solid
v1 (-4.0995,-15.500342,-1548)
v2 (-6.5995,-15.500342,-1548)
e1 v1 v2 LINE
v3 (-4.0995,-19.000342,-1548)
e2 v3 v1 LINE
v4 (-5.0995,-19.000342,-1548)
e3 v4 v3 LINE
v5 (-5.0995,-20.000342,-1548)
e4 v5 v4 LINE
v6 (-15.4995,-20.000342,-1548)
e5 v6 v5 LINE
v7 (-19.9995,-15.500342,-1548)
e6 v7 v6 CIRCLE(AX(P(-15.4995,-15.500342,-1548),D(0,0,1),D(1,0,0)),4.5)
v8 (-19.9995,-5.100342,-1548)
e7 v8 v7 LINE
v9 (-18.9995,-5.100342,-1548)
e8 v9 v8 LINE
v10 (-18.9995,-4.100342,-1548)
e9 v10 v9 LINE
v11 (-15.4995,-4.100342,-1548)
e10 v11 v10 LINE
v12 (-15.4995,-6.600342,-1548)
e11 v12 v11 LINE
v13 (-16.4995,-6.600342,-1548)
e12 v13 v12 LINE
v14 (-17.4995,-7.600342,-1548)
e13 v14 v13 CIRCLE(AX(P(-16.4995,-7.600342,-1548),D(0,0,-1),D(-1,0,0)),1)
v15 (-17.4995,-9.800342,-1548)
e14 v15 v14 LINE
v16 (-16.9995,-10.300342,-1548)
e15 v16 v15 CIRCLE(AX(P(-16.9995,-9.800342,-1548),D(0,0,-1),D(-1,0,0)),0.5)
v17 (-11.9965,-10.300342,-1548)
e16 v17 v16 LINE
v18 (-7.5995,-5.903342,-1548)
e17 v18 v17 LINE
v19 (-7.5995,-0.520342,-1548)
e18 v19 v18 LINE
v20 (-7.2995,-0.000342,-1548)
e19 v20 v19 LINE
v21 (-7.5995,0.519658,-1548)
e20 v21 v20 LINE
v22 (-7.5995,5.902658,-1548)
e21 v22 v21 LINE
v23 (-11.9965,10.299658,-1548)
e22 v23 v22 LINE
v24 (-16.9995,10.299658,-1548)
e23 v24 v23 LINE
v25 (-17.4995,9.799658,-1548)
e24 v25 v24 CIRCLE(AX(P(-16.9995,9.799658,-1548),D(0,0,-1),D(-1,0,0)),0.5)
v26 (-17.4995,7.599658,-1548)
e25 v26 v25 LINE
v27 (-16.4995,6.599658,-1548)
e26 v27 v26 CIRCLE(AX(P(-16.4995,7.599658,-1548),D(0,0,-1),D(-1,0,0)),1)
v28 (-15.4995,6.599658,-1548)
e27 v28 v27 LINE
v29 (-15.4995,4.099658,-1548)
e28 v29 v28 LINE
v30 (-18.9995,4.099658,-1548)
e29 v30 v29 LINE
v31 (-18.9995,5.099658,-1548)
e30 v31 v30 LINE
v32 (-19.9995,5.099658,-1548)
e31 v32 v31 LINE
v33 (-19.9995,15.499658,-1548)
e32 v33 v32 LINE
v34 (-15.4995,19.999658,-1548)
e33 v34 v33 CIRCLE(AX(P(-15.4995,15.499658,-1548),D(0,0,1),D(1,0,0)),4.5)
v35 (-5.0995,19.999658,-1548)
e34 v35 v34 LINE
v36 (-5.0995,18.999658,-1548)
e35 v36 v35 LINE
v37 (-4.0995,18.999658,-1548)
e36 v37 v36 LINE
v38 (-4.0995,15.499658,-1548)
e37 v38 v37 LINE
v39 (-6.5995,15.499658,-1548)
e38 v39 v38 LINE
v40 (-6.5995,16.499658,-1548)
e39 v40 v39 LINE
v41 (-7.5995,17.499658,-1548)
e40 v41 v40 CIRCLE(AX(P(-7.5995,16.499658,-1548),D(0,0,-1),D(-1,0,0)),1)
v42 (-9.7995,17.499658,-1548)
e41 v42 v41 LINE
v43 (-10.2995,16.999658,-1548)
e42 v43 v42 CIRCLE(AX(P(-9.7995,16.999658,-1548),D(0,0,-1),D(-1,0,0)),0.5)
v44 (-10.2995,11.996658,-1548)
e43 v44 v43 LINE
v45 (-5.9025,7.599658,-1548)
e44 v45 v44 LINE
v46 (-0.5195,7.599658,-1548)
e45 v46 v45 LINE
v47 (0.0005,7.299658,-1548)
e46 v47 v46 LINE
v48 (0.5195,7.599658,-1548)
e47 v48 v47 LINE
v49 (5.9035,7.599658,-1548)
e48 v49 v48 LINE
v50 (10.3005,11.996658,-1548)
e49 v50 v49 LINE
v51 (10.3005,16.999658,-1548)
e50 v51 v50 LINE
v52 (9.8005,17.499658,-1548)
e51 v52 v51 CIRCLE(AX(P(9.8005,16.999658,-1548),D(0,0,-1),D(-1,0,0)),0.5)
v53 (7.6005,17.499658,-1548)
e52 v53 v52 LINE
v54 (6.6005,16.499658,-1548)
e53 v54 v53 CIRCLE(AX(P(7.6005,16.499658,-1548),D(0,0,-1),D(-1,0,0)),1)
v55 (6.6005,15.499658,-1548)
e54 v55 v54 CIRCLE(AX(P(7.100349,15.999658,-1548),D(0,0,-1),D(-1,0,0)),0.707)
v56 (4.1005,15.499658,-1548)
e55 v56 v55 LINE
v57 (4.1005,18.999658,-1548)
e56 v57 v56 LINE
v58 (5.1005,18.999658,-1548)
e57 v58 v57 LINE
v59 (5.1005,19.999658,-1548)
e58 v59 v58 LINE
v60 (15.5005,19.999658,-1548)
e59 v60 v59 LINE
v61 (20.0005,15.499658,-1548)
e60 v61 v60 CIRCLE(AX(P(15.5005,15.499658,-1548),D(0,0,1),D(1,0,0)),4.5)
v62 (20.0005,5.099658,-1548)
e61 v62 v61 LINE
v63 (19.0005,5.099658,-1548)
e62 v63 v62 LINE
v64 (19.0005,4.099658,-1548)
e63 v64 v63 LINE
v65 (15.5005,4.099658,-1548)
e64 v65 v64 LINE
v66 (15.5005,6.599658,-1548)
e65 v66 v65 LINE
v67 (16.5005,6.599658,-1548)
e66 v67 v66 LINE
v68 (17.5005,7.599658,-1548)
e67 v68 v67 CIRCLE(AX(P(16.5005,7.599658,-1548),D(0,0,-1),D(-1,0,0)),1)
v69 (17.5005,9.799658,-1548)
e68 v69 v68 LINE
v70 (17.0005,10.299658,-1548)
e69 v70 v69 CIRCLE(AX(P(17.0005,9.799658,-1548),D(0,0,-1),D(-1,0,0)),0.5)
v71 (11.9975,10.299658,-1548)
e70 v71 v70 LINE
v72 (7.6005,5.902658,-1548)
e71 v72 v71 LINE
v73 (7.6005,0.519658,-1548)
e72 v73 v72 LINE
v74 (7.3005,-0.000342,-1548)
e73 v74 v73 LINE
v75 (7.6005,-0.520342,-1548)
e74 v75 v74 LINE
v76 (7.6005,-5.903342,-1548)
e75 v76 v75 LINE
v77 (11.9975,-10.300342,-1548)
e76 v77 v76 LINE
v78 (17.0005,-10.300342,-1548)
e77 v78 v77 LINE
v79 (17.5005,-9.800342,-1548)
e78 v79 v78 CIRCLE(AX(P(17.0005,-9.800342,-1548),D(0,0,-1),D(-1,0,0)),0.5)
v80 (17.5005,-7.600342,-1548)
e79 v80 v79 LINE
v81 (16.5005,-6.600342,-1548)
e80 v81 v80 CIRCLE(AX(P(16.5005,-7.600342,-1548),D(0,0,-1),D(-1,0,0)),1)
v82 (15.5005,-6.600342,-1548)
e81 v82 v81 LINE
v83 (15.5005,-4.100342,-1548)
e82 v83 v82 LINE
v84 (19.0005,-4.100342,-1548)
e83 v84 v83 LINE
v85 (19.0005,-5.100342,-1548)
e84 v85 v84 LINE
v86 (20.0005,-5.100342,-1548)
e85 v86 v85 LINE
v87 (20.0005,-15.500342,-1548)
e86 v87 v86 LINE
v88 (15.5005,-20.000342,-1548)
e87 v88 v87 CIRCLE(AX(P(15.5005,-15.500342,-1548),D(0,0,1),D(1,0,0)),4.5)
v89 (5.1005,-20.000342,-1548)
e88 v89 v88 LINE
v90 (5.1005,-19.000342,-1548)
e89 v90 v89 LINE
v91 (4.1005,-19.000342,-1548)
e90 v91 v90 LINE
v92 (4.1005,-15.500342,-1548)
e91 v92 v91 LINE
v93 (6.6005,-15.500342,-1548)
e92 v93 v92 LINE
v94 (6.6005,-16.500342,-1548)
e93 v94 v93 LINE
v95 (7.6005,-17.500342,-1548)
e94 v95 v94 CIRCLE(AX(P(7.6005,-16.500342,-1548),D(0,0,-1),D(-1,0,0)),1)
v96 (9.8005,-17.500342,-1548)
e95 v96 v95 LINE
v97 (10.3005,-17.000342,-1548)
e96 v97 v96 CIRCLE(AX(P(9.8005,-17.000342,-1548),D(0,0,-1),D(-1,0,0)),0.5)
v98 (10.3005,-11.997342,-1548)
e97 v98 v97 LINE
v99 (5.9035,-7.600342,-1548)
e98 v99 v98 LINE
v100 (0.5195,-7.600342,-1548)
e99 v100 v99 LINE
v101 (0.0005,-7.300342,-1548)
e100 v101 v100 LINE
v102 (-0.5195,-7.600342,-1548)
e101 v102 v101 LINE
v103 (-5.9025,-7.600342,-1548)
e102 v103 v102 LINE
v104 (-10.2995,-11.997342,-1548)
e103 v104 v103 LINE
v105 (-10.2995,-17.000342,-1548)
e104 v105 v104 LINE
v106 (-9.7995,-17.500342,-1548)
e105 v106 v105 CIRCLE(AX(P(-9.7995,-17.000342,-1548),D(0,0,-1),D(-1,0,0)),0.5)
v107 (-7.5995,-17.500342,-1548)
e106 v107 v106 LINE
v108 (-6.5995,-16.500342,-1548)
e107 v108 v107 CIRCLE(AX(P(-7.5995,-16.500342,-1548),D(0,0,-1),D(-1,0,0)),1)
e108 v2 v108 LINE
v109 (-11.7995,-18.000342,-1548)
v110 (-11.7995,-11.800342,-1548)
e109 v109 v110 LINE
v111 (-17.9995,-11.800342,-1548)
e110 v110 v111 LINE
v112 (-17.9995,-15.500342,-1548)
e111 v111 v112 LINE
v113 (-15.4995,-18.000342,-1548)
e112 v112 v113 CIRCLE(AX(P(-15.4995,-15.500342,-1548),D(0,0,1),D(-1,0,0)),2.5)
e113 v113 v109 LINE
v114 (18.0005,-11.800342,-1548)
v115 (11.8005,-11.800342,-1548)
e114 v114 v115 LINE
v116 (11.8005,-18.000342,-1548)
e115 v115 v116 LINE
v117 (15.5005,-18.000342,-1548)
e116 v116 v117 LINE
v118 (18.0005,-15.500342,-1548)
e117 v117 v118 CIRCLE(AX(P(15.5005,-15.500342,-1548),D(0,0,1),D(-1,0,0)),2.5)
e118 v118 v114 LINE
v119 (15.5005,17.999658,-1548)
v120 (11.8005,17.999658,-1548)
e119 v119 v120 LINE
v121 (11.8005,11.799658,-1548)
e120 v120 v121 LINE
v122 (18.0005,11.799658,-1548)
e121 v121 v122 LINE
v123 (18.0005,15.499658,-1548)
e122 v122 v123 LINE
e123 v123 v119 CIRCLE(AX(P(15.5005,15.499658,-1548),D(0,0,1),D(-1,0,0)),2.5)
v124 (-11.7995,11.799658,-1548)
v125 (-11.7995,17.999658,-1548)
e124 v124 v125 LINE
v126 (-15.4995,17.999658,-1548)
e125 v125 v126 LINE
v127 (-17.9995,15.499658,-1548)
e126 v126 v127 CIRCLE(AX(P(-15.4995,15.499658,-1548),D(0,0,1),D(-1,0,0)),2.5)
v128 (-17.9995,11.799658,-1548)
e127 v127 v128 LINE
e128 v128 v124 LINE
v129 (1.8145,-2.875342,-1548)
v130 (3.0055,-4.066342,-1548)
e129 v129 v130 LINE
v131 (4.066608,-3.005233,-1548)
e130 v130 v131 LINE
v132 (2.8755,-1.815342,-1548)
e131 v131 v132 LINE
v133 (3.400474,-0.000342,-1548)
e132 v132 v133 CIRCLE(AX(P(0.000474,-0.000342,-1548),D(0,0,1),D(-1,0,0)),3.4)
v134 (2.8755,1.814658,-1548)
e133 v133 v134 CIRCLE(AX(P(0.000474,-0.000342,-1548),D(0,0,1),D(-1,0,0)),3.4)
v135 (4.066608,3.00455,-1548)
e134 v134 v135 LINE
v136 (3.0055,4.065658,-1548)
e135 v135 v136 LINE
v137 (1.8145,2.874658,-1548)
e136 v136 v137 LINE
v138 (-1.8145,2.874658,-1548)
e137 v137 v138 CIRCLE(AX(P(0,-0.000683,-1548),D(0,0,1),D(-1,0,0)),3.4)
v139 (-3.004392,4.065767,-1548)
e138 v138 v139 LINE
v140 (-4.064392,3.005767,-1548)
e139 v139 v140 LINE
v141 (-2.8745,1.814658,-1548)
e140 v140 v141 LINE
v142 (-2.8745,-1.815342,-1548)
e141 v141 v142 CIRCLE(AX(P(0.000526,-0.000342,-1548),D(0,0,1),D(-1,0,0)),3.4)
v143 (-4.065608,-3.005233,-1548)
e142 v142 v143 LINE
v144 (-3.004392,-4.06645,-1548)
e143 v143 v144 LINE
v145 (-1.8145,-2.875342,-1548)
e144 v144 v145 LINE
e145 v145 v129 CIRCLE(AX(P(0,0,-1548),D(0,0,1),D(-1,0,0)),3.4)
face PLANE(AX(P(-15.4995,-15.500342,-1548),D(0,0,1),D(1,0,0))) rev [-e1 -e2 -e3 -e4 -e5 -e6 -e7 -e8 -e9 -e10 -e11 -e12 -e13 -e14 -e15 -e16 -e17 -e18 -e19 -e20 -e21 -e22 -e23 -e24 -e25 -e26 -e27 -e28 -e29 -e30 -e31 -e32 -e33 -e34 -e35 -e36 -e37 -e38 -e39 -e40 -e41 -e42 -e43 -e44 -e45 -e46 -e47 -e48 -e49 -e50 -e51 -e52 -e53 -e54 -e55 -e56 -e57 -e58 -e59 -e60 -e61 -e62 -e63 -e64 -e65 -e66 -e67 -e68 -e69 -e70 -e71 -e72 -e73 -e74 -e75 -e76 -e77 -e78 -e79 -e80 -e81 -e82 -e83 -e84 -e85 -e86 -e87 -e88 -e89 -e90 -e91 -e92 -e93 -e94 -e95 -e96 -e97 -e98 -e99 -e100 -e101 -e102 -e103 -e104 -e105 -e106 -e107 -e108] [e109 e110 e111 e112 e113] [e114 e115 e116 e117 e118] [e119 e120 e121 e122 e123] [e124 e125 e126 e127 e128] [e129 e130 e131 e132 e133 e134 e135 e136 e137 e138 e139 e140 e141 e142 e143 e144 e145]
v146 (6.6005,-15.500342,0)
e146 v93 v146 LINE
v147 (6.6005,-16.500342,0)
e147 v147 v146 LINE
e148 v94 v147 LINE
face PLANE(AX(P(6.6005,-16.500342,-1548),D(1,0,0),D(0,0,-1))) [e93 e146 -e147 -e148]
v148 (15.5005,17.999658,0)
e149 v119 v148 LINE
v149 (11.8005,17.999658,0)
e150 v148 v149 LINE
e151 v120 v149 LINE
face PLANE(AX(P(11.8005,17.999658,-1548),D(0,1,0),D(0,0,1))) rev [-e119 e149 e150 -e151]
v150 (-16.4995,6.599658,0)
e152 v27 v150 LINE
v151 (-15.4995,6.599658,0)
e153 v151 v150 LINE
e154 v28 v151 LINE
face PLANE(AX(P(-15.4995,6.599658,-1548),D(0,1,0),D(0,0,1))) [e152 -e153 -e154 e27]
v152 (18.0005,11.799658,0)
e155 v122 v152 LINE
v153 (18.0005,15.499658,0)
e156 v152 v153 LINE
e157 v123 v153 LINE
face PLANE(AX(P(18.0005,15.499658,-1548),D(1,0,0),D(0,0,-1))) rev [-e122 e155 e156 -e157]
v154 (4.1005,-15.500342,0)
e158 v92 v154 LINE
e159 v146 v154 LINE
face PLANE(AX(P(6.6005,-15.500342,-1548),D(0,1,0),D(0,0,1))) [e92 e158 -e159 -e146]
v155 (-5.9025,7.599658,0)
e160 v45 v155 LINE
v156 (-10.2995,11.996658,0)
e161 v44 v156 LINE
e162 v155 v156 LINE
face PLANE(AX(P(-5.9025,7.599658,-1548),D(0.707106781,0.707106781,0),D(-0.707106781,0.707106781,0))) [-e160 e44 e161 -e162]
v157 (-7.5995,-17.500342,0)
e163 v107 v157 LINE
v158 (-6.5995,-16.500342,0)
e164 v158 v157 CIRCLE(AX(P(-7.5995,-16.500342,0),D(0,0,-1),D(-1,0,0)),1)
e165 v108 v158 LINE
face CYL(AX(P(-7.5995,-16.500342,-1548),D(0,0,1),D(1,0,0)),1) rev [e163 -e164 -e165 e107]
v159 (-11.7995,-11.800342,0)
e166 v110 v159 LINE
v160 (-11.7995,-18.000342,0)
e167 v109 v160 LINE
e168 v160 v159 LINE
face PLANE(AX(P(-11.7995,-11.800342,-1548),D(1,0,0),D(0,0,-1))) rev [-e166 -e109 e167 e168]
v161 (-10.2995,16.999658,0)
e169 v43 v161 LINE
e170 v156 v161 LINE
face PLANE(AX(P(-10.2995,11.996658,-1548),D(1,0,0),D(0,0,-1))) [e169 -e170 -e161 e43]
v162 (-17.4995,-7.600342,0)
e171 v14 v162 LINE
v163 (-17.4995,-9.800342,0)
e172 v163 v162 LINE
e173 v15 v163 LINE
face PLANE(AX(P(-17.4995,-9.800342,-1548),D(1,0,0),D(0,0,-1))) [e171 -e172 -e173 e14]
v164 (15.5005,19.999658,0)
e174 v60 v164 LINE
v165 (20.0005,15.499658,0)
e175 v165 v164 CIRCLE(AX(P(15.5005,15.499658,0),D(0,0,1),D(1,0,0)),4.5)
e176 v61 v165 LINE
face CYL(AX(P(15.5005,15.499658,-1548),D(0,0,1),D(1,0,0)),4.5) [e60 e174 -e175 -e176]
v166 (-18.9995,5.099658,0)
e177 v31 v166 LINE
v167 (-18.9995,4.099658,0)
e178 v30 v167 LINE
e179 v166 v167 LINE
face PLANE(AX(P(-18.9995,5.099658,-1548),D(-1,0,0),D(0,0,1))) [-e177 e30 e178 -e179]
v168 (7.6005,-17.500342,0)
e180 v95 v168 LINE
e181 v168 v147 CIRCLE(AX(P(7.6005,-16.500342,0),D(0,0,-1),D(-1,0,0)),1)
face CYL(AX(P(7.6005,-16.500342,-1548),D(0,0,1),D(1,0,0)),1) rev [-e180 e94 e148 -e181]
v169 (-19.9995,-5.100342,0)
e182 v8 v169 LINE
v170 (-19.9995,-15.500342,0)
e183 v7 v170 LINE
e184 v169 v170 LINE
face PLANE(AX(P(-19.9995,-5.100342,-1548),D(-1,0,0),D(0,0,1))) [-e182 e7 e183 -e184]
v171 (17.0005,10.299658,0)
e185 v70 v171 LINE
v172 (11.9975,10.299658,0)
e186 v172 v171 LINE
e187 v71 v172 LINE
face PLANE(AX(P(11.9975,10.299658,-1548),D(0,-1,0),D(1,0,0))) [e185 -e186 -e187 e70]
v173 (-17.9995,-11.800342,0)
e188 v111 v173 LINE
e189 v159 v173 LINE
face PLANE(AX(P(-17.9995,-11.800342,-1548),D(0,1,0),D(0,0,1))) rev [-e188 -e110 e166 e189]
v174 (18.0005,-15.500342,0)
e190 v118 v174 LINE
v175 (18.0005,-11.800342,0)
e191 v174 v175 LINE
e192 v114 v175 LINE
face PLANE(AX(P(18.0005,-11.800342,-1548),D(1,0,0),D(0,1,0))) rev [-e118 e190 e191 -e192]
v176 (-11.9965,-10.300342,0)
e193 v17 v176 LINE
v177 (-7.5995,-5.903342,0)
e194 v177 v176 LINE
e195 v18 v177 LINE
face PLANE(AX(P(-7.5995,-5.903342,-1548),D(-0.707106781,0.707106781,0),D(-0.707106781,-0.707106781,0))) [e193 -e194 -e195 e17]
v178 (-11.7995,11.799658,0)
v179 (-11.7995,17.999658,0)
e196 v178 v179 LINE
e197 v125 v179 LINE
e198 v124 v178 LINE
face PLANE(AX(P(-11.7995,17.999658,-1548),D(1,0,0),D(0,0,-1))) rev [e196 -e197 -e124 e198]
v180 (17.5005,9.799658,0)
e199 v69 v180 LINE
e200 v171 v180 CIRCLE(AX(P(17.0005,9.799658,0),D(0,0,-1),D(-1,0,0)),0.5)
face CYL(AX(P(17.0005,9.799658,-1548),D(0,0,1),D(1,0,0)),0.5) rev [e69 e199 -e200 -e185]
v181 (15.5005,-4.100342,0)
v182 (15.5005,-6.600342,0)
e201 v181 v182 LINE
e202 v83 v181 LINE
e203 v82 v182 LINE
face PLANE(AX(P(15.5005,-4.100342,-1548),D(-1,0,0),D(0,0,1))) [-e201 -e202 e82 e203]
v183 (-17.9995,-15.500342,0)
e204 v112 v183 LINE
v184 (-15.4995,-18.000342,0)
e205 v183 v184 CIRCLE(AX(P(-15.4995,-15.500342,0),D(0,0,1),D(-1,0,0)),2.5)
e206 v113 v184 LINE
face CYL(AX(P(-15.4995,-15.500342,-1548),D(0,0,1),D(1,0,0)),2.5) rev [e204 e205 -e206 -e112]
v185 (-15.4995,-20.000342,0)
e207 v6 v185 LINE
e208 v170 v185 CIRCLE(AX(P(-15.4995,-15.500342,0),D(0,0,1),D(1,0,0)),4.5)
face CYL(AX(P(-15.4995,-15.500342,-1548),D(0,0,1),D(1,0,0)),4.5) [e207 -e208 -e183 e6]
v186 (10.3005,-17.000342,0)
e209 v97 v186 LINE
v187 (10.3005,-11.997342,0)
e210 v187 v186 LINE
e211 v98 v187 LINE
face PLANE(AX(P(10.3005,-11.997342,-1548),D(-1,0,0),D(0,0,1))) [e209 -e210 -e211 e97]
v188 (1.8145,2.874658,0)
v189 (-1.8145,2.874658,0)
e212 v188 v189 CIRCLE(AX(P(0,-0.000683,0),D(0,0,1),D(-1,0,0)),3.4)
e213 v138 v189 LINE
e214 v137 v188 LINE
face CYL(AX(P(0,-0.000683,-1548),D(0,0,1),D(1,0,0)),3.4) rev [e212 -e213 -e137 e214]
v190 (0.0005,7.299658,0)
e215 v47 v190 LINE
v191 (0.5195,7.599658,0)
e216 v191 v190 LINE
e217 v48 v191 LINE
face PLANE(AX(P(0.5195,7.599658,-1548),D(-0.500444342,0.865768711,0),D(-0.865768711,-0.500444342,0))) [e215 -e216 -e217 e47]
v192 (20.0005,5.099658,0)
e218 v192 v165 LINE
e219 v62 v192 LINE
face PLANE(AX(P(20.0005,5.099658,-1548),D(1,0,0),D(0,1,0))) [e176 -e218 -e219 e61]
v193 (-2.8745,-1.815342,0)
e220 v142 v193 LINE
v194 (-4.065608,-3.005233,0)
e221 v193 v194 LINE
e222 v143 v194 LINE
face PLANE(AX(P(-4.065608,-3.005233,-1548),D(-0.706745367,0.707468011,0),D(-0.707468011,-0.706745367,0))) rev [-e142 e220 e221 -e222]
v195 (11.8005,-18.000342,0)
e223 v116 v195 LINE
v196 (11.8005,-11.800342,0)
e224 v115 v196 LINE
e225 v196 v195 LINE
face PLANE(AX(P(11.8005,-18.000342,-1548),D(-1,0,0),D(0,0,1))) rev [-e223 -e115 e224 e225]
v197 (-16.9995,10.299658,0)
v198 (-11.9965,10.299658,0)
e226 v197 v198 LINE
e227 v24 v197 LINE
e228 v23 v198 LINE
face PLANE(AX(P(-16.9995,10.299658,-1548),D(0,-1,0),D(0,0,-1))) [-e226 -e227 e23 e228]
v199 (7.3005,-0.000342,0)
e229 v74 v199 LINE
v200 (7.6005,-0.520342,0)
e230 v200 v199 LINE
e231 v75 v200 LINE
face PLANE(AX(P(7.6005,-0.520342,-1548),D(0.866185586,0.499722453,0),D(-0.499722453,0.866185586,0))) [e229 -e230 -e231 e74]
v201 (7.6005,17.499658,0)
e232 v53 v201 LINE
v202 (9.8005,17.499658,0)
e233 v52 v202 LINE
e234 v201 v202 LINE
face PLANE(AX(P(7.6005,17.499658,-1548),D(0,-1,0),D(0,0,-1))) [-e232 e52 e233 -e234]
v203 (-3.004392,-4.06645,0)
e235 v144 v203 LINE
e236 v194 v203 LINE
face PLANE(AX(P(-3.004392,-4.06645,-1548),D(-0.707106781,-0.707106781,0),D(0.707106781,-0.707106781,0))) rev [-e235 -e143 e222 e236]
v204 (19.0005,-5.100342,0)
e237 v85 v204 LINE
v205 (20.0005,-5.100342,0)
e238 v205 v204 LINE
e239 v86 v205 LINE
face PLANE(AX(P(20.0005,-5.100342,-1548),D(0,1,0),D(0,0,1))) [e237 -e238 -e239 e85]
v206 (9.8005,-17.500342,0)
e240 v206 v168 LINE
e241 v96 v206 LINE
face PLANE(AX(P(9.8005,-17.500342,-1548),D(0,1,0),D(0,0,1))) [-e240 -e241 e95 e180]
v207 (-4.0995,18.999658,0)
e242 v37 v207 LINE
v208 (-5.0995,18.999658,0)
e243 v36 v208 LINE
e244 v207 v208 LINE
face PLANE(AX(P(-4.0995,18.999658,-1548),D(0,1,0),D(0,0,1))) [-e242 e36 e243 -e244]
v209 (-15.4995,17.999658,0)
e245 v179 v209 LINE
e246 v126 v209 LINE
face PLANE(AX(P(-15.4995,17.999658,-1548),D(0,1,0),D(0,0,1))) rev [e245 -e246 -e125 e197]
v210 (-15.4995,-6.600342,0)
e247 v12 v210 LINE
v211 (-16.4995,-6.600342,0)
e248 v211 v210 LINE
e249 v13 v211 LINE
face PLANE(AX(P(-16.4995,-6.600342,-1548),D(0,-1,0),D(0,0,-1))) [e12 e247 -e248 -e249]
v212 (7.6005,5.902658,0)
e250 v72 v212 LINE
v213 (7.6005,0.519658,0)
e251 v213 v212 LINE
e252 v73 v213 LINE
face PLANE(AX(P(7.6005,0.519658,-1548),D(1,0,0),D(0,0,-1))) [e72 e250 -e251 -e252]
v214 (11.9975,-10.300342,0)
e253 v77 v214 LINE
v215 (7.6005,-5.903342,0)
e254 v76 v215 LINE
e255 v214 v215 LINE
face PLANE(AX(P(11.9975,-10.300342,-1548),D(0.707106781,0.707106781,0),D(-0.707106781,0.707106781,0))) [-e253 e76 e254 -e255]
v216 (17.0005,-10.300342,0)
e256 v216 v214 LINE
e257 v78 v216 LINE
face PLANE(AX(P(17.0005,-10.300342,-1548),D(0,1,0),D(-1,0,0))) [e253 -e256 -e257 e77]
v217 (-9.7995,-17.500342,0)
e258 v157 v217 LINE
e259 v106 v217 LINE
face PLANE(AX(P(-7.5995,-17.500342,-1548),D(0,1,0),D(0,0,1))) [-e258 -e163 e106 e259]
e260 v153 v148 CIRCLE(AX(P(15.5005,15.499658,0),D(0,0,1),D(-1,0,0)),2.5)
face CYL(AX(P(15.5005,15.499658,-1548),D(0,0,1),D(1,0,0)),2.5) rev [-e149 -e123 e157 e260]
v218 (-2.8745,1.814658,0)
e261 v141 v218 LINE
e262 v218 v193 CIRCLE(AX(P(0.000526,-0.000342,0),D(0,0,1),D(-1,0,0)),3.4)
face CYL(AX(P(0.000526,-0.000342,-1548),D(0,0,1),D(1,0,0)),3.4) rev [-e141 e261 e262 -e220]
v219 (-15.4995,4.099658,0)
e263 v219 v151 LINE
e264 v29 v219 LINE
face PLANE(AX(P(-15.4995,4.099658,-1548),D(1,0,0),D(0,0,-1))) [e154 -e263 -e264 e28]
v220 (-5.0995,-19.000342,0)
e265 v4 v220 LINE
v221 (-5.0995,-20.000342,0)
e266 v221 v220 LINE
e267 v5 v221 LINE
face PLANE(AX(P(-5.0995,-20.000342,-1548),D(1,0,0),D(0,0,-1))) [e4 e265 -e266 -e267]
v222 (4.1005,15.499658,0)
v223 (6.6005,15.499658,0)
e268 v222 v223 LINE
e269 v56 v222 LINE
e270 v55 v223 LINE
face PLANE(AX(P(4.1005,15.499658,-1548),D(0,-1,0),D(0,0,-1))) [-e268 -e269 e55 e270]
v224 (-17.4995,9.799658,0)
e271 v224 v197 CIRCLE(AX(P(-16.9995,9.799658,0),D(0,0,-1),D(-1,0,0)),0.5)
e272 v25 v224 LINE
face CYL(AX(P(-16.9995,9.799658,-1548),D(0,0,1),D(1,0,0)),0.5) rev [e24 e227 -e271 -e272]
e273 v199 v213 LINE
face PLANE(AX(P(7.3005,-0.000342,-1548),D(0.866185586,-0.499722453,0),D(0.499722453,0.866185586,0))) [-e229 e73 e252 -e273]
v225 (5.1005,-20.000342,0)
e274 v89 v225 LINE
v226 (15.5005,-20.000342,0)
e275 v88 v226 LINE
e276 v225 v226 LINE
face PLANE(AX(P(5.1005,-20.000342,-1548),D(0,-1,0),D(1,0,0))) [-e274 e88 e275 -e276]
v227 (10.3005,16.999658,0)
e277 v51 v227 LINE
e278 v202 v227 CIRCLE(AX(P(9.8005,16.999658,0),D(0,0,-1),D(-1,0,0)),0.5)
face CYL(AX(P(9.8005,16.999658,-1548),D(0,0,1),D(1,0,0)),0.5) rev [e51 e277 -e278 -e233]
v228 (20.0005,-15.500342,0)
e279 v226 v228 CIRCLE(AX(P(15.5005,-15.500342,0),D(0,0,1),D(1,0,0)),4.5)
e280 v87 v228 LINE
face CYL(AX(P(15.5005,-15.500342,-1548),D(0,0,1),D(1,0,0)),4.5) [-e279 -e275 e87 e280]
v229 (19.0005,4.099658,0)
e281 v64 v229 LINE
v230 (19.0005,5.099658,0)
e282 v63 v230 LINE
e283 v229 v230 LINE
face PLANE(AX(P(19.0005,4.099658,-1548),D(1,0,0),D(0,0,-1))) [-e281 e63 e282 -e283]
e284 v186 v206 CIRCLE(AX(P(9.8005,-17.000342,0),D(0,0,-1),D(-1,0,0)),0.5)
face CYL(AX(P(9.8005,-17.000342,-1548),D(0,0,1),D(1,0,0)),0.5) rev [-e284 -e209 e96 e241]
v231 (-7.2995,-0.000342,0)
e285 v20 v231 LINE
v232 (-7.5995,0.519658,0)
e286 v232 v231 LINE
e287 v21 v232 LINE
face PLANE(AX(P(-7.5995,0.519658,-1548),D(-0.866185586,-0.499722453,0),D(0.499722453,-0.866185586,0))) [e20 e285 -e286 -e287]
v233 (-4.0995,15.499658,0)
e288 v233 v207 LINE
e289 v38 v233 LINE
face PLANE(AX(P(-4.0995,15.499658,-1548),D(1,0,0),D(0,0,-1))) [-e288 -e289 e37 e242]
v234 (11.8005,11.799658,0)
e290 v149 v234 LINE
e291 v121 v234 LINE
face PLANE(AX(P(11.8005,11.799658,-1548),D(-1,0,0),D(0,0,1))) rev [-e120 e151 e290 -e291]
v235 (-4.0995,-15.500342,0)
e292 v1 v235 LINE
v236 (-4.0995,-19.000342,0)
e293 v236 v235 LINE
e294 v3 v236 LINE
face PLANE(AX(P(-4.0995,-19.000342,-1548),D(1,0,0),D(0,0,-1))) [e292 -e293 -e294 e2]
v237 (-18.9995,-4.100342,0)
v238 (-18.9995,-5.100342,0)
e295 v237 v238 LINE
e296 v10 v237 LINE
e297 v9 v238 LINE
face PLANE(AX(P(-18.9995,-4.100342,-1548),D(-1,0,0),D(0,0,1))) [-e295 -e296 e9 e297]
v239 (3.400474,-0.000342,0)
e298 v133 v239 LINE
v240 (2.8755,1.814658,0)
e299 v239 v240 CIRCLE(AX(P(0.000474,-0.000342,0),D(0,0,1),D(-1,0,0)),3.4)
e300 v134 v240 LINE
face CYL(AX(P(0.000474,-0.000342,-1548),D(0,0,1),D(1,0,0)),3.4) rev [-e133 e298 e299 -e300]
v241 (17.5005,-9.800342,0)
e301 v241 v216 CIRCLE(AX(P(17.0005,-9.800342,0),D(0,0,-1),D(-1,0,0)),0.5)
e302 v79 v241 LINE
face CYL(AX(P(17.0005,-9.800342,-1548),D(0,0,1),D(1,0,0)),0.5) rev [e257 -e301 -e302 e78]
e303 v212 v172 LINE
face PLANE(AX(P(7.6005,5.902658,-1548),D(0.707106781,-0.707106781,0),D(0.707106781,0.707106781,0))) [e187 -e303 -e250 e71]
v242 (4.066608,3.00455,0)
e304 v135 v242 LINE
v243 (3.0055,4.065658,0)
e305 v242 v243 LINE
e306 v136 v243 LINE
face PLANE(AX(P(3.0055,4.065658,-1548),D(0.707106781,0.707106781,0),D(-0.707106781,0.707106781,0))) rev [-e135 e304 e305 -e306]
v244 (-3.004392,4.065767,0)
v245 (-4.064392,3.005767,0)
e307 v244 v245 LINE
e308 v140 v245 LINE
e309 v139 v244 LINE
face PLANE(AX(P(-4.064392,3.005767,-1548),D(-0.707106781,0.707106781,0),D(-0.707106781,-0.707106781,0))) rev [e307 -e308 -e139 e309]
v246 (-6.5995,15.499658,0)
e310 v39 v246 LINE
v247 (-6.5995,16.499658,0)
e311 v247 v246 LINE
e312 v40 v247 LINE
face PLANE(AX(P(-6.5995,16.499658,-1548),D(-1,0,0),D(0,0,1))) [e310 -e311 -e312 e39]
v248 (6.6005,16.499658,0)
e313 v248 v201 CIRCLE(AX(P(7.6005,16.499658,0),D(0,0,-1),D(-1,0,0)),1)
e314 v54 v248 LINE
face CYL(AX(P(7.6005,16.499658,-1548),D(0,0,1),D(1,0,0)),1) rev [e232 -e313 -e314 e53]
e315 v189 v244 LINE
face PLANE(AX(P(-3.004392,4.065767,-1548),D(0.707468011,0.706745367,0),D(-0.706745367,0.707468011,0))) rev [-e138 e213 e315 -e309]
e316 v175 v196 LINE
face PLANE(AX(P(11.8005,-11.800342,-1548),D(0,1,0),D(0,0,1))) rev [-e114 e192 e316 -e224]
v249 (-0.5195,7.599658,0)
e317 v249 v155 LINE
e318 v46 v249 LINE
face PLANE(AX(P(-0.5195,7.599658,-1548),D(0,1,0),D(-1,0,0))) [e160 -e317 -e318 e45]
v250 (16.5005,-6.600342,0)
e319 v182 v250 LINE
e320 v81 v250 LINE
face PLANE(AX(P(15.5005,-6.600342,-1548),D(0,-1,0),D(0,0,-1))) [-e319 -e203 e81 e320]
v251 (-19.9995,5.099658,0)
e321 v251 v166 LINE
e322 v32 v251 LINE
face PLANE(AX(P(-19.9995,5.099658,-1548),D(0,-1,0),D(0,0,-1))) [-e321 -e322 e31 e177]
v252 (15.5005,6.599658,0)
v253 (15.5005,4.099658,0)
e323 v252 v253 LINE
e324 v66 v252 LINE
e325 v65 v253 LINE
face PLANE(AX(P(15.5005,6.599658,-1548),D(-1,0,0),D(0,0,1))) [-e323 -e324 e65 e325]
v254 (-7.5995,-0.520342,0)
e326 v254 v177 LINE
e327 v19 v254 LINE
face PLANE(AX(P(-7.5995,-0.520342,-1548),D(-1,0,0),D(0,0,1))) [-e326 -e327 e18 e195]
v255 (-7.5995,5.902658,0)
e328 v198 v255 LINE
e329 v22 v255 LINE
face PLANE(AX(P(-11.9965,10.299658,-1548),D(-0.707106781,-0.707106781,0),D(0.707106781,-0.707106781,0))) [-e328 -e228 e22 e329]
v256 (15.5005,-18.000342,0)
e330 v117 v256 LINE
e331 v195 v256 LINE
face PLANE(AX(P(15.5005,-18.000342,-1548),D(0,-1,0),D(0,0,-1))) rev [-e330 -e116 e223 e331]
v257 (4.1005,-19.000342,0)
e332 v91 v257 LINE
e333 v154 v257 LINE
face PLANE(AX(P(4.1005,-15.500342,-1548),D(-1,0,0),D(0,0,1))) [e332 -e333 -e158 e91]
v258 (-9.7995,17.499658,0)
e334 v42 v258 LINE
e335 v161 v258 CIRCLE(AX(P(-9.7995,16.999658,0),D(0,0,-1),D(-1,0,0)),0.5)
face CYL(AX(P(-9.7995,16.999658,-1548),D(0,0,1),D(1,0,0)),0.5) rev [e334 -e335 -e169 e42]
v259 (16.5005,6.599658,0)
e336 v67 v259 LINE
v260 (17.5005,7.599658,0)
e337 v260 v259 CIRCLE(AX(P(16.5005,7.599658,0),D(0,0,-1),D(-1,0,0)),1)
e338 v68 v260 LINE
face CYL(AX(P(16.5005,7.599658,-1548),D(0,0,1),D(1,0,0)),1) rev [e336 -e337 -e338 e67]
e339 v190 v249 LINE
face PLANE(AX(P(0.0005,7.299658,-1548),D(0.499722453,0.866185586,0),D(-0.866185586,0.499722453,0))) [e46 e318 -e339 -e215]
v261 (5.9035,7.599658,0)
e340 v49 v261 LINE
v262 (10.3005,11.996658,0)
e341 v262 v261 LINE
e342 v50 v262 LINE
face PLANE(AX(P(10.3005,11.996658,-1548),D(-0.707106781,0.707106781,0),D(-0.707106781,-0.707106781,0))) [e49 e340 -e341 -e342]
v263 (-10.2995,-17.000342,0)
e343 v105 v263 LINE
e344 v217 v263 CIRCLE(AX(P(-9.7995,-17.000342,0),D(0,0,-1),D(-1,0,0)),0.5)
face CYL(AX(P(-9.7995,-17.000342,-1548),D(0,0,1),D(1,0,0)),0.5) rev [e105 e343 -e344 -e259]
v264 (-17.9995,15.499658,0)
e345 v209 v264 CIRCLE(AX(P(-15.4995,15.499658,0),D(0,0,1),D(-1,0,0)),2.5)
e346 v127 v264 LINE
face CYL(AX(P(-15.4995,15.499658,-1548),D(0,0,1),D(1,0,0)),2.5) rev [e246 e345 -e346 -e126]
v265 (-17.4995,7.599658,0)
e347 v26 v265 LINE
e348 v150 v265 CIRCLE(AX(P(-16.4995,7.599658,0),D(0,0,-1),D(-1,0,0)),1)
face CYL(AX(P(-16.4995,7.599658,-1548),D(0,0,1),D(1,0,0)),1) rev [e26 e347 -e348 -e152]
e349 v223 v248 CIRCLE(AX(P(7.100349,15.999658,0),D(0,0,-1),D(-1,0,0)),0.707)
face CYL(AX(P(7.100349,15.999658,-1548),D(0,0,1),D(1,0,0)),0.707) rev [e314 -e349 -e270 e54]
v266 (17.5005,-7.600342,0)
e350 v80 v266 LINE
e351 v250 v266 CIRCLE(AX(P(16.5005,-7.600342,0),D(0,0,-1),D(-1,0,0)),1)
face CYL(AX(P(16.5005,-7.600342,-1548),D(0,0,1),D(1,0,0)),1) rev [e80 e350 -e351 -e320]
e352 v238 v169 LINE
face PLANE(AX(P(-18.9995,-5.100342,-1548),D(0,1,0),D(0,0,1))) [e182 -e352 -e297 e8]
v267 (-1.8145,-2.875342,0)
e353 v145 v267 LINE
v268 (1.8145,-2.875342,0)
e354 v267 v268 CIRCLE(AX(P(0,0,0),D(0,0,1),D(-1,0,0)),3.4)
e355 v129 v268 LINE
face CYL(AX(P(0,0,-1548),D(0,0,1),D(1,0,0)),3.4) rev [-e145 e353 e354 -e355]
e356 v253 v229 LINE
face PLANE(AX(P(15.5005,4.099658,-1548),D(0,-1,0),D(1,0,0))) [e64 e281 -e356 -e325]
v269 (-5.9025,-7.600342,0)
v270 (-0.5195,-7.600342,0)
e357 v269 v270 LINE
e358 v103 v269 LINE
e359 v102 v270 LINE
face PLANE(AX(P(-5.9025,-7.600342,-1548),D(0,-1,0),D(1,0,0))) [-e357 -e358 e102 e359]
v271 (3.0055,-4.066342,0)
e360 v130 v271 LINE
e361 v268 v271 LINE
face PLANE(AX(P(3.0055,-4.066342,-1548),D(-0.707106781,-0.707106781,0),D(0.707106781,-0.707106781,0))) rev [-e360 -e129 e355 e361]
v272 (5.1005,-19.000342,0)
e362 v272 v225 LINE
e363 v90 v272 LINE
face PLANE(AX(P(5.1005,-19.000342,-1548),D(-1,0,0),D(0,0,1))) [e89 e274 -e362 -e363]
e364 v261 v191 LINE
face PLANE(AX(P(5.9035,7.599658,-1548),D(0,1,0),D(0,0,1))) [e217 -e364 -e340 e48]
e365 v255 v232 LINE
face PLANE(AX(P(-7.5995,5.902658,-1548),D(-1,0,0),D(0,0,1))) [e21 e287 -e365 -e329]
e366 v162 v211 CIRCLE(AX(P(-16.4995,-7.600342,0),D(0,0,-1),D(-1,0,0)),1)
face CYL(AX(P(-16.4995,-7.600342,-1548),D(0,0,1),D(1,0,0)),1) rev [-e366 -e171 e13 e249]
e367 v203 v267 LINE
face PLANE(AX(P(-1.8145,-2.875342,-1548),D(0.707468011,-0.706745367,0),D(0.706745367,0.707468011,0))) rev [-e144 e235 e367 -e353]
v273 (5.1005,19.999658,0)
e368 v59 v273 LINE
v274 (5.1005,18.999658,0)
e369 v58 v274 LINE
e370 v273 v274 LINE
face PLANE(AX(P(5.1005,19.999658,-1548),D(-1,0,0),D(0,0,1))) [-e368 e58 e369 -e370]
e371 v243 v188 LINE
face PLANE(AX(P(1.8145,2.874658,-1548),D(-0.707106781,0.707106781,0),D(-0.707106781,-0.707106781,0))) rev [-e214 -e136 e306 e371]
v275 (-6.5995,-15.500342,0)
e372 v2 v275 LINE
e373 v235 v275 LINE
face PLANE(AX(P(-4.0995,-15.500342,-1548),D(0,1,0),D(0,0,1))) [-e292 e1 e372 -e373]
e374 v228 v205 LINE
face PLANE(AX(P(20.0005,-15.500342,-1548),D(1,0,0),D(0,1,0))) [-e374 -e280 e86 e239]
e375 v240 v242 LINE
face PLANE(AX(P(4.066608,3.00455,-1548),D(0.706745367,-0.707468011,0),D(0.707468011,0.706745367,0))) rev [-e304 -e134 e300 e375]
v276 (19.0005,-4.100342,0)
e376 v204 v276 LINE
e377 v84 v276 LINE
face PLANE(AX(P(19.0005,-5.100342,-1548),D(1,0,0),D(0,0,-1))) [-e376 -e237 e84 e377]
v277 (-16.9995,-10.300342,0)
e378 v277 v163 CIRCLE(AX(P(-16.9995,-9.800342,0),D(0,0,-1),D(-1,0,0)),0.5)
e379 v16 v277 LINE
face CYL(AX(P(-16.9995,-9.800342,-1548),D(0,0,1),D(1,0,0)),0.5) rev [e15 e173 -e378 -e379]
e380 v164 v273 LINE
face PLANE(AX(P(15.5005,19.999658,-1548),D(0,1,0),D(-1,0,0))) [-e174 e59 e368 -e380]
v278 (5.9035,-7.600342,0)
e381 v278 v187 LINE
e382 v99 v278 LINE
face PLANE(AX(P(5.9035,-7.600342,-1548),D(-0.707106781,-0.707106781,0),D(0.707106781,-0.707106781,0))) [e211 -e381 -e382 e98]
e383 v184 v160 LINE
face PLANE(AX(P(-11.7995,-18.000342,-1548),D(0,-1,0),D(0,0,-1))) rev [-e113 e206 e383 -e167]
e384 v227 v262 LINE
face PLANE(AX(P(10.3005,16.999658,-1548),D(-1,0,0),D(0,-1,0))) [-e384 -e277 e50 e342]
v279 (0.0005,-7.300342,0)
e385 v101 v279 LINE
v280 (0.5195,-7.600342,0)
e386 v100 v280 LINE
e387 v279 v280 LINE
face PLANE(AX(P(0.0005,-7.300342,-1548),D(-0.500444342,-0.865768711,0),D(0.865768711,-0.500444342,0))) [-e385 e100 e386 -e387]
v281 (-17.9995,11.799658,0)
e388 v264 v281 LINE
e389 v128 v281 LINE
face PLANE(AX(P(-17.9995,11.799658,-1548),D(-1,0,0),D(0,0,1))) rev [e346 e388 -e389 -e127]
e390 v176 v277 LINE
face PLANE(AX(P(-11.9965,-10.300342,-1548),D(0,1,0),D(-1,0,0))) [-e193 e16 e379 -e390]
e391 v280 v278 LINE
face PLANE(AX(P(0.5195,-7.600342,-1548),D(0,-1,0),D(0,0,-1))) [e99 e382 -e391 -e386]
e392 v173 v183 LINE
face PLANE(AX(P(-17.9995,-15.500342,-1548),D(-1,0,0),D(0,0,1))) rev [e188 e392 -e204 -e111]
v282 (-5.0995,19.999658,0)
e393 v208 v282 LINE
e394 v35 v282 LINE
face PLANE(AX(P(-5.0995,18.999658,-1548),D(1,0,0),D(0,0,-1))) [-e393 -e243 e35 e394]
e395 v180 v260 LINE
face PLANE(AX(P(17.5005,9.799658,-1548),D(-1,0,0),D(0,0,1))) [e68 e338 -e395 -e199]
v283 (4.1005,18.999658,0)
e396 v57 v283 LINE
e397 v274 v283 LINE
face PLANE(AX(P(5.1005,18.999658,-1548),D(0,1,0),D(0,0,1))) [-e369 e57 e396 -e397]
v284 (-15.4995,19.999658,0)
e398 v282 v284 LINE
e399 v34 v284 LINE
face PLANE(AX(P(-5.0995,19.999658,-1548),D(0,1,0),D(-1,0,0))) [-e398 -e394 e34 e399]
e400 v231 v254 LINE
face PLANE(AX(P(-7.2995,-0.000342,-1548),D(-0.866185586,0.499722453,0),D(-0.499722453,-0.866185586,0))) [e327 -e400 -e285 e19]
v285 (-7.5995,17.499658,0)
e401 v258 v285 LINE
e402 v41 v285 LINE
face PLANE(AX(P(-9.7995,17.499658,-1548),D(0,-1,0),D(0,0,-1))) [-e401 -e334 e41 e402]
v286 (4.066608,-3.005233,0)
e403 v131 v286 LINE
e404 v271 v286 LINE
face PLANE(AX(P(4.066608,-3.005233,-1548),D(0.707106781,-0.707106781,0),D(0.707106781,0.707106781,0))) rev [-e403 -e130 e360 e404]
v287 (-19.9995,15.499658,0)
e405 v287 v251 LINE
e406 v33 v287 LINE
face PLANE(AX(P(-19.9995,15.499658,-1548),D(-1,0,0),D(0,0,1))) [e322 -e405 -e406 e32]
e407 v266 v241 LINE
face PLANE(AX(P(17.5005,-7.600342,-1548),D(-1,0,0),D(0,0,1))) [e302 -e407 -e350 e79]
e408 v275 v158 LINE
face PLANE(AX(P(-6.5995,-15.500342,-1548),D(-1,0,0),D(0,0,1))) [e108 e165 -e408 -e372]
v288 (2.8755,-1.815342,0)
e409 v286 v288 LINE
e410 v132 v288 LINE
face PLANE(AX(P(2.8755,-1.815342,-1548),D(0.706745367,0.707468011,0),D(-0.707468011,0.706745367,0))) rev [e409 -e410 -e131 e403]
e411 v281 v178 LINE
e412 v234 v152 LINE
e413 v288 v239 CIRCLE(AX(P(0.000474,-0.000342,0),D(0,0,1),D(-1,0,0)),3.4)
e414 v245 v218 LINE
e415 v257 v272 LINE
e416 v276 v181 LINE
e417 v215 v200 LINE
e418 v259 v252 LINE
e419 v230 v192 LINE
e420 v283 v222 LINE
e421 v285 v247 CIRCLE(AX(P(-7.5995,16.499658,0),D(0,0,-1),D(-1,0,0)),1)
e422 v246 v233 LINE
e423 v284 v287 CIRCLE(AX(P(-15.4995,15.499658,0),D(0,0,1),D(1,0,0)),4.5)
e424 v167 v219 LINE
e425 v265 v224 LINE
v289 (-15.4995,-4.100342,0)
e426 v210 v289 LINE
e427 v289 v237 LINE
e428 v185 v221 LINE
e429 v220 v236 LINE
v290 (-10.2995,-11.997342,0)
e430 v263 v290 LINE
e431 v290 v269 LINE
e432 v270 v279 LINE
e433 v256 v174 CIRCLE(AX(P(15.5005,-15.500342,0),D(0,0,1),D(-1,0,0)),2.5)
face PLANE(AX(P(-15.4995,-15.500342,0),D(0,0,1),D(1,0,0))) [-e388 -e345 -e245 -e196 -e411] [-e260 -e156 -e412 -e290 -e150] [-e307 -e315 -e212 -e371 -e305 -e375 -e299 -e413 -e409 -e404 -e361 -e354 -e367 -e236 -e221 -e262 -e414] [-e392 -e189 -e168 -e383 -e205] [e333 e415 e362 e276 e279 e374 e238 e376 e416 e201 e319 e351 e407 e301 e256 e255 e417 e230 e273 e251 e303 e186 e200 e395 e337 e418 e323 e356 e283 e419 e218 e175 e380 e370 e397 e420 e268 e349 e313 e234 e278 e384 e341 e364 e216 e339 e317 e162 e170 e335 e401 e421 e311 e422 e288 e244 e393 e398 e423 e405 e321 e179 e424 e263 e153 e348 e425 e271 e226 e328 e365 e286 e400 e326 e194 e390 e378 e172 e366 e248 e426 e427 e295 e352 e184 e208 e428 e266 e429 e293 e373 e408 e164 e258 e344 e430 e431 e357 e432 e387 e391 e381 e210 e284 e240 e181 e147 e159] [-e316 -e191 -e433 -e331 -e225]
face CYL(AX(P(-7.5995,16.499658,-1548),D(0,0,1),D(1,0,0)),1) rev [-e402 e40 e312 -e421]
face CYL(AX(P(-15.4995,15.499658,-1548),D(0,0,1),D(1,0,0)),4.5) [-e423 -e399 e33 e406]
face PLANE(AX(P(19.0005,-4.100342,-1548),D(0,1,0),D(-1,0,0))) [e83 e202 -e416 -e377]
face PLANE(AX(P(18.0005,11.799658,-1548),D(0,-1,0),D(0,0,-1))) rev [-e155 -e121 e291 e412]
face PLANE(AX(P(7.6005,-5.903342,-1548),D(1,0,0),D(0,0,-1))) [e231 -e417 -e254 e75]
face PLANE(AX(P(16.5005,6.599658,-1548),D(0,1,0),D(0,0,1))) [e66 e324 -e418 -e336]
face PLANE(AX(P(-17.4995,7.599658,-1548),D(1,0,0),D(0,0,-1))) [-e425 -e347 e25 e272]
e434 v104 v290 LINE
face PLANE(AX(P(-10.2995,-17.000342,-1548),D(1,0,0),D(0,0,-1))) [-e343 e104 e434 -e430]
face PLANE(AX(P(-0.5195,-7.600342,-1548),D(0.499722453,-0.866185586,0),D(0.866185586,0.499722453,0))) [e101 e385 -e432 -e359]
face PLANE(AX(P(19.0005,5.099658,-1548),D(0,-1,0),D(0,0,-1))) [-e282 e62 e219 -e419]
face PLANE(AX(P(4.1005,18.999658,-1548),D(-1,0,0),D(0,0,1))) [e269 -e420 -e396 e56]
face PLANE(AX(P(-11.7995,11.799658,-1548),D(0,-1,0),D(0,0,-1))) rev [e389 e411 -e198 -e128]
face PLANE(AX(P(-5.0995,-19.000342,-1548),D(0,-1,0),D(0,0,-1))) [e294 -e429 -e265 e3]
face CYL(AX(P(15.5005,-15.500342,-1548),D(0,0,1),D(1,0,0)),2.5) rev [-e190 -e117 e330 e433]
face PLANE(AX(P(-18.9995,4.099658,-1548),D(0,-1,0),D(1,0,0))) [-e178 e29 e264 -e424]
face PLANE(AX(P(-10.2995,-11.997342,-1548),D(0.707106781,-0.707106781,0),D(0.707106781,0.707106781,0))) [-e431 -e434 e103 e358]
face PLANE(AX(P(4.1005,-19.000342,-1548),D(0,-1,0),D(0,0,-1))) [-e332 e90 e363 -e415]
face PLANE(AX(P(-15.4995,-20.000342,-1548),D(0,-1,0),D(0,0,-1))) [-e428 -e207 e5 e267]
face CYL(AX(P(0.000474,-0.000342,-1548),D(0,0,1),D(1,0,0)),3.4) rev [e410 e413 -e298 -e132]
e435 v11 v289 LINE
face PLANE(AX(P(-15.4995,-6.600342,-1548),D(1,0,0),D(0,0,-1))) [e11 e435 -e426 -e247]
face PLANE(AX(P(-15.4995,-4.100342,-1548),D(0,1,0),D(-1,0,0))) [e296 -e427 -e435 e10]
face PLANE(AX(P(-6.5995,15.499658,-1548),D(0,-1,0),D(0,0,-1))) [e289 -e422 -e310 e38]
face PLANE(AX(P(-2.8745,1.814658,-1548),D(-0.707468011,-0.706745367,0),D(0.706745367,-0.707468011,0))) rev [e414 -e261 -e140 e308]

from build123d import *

# Parameters (mm, degrees)
EXTRUDE_1_DEPTH = 1548


with BuildPart() as part:
    # 草图1 → 凸台-拉伸1 (new body)
    with BuildSketch(Plane.XY):
        with BuildLine():
            Line((-18.9995, -4.100341675), (-18.9995, -5.100341675))
            Line((-18.9995, -5.100341675), (-19.9995, -5.100341675))
            Line((-19.9995, -5.100341675), (-19.9995, -15.500341675))
            ThreePointArc((-19.9995, -15.500341675), (-18.681480515, -18.682322191), (-15.4995, -20.000341675))
            Line((-15.4995, -20.000341675), (-5.0995, -20.000341675))
            Line((-5.0995, -20.000341675), (-5.0995, -19.000341675))
            Line((-5.0995, -19.000341675), (-4.0995, -19.000341675))
            Line((-4.0995, -19.000341675), (-4.0995, -15.500341675))
            Line((-4.0995, -15.500341675), (-6.5995, -15.500341675))
            Line((-6.5995, -15.500341675), (-6.5995, -16.500341675))
            ThreePointArc((-6.5995, -16.500341675), (-6.892393219, -17.207448457), (-7.5995, -17.500341675))
            Line((-7.5995, -17.500341675), (-9.7995, -17.500341675))
            ThreePointArc((-9.7995, -17.500341675), (-10.153053391, -17.353895066), (-10.2995, -17.000341675))
            Line((-10.2995, -17.000341675), (-10.2995, -11.997341675))
            Line((-10.2995, -11.997341675), (-5.9025, -7.600341675))
            Line((-5.9025, -7.600341675), (-0.5195, -7.600341675))
            Line((-0.5195, -7.600341675), (0.0005, -7.300341675))
            Line((0.0005, -7.300341675), (0.5195, -7.600341675))
            Line((0.5195, -7.600341675), (5.9035, -7.600341675))
            Line((5.9035, -7.600341675), (10.3005, -11.997341675))
            Line((10.3005, -11.997341675), (10.3005, -17.000341675))
            ThreePointArc((10.3005, -17.000341675), (10.154053391, -17.353895066), (9.8005, -17.500341675))
            Line((9.8005, -17.500341675), (7.6005, -17.500341675))
            ThreePointArc((7.6005, -17.500341675), (6.893393219, -17.207448457), (6.6005, -16.500341675))
            Line((6.6005, -16.500341675), (6.6005, -15.500341675))
            Line((6.6005, -15.500341675), (4.1005, -15.500341675))
            Line((4.1005, -15.500341675), (4.1005, -19.000341675))
            Line((4.1005, -19.000341675), (5.1005, -19.000341675))
            Line((5.1005, -19.000341675), (5.1005, -20.000341675))
            Line((5.1005, -20.000341675), (15.5005, -20.000341675))
            ThreePointArc((15.5005, -20.000341675), (18.682480515, -18.682322191), (20.0005, -15.500341675))
            Line((20.0005, -15.500341675), (20.0005, -5.100341675))
            Line((20.0005, -5.100341675), (19.0005, -5.100341675))
            Line((19.0005, -5.100341675), (19.0005, -4.100341675))
            Line((19.0005, -4.100341675), (15.5005, -4.100341675))
            Line((15.5005, -4.100341675), (15.5005, -6.600341675))
            Line((15.5005, -6.600341675), (16.5005, -6.600341675))
            ThreePointArc((16.5005, -6.600341675), (17.207606781, -6.893234894), (17.5005, -7.600341675))
            Line((17.5005, -7.600341675), (17.5005, -9.800341675))
            ThreePointArc((17.5005, -9.800341675), (17.354053391, -10.153895066), (17.0005, -10.300341675))
            Line((17.0005, -10.300341675), (11.9975, -10.300341675))
            Line((11.9975, -10.300341675), (7.6005, -5.903341675))
            Line((7.6005, -5.903341675), (7.6005, -0.520341675))
            Line((7.6005, -0.520341675), (7.3005, -0.000341675))
            Line((7.3005, -0.000341675), (7.6005, 0.519658325))
            Line((7.6005, 0.519658325), (7.6005, 5.902658325))
            Line((7.6005, 5.902658325), (11.9975, 10.299658325))
            Line((11.9975, 10.299658325), (17.0005, 10.299658325))
            ThreePointArc((17.0005, 10.299658325), (17.354053391, 10.153211715), (17.5005, 9.799658325))
            Line((17.5005, 9.799658325), (17.5005, 7.599658325))
            ThreePointArc((17.5005, 7.599658325), (17.207606781, 6.892551543), (16.5005, 6.599658325))
            Line((16.5005, 6.599658325), (15.5005, 6.599658325))
            Line((15.5005, 6.599658325), (15.5005, 4.099658325))
            Line((15.5005, 4.099658325), (19.0005, 4.099658325))
            Line((19.0005, 4.099658325), (19.0005, 5.099658325))
            Line((19.0005, 5.099658325), (20.0005, 5.099658325))
            Line((20.0005, 5.099658325), (20.0005, 15.499658325))
            ThreePointArc((20.0005, 15.499658325), (18.682480515, 18.68163884), (15.5005, 19.999658325))
            Line((15.5005, 19.999658325), (5.1005, 19.999658325))
            Line((5.1005, 19.999658325), (5.1005, 18.999658325))
            Line((5.1005, 18.999658325), (4.1005, 18.999658325))
            Line((4.1005, 18.999658325), (4.1005, 15.499658325))
            Line((4.1005, 15.499658325), (6.6005, 15.499658325))
            ThreePointArc((6.6005, 15.499658325), (6.393348977, 15.999658325), (6.6005, 16.499658325))
            ThreePointArc((6.6005, 16.499658325), (6.893393219, 17.206765106), (7.6005, 17.499658325))
            Line((7.6005, 17.499658325), (9.8005, 17.499658325))
            ThreePointArc((9.8005, 17.499658325), (10.154053391, 17.353211715), (10.3005, 16.999658325))
            Line((10.3005, 16.999658325), (10.3005, 11.996658325))
            Line((10.3005, 11.996658325), (5.9035, 7.599658325))
            Line((5.9035, 7.599658325), (0.5195, 7.599658325))
            Line((0.5195, 7.599658325), (0.0005, 7.299658325))
            Line((0.0005, 7.299658325), (-0.5195, 7.599658325))
            Line((-0.5195, 7.599658325), (-5.9025, 7.599658325))
            Line((-5.9025, 7.599658325), (-10.2995, 11.996658325))
            Line((-10.2995, 11.996658325), (-10.2995, 16.999658325))
            ThreePointArc((-10.2995, 16.999658325), (-10.153053391, 17.353211715), (-9.7995, 17.499658325))
            Line((-9.7995, 17.499658325), (-7.5995, 17.499658325))
            ThreePointArc((-7.5995, 17.499658325), (-6.892393219, 17.206765106), (-6.5995, 16.499658325))
            Line((-6.5995, 16.499658325), (-6.5995, 15.499658325))
            Line((-6.5995, 15.499658325), (-4.0995, 15.499658325))
            Line((-4.0995, 15.499658325), (-4.0995, 18.999658325))
            Line((-4.0995, 18.999658325), (-5.0995, 18.999658325))
            Line((-5.0995, 18.999658325), (-5.0995, 19.999658325))
            Line((-5.0995, 19.999658325), (-15.4995, 19.999658325))
            ThreePointArc((-15.4995, 19.999658325), (-18.681480515, 18.68163884), (-19.9995, 15.499658325))
            Line((-19.9995, 15.499658325), (-19.9995, 5.099658325))
            Line((-19.9995, 5.099658325), (-18.9995, 5.099658325))
            Line((-18.9995, 5.099658325), (-18.9995, 4.099658325))
            Line((-18.9995, 4.099658325), (-15.4995, 4.099658325))
            Line((-15.4995, 4.099658325), (-15.4995, 6.599658325))
            Line((-15.4995, 6.599658325), (-16.4995, 6.599658325))
            ThreePointArc((-16.4995, 6.599658325), (-17.206606781, 6.892551543), (-17.4995, 7.599658325))
            Line((-17.4995, 7.599658325), (-17.4995, 9.799658325))
            ThreePointArc((-17.4995, 9.799658325), (-17.353053391, 10.153211715), (-16.9995, 10.299658325))
            Line((-16.9995, 10.299658325), (-11.9965, 10.299658325))
            Line((-11.9965, 10.299658325), (-7.5995, 5.902658325))
            Line((-7.5995, 5.902658325), (-7.5995, 0.519658325))
            Line((-7.5995, 0.519658325), (-7.2995, -0.000341675))
            Line((-7.2995, -0.000341675), (-7.5995, -0.520341675))
            Line((-7.5995, -0.520341675), (-7.5995, -5.903341675))
            Line((-7.5995, -5.903341675), (-11.9965, -10.300341675))
            Line((-11.9965, -10.300341675), (-16.9995, -10.300341675))
            ThreePointArc((-16.9995, -10.300341675), (-17.353053391, -10.153895066), (-17.4995, -9.800341675))
            Line((-17.4995, -9.800341675), (-17.4995, -7.600341675))
            ThreePointArc((-17.4995, -7.600341675), (-17.206606781, -6.893234894), (-16.4995, -6.600341675))
            Line((-16.4995, -6.600341675), (-15.4995, -6.600341675))
            Line((-15.4995, -6.600341675), (-15.4995, -4.100341675))
            Line((-15.4995, -4.100341675), (-18.9995, -4.100341675))
        make_face()
        with BuildLine():
            Line((15.5005, -18.000341675), (11.8005, -18.000341675))
            Line((11.8005, -18.000341675), (11.8005, -11.800341675))
            Line((11.8005, -11.800341675), (18.0005, -11.800341675))
            Line((18.0005, -11.800341675), (18.0005, -15.500341675))
            ThreePointArc((18.0005, -15.500341675), (17.268266953, -17.268108628), (15.5005, -18.000341675))
        make_face(mode=Mode.SUBTRACT)
        with BuildLine():
            Line((18.0005, 11.799658325), (11.8005, 11.799658325))
            Line((11.8005, 11.799658325), (11.8005, 17.999658325))
            Line((11.8005, 17.999658325), (15.5005, 17.999658325))
            ThreePointArc((15.5005, 17.999658325), (17.268266953, 17.267425278), (18.0005, 15.499658325))
            Line((18.0005, 15.499658325), (18.0005, 11.799658325))
        make_face(mode=Mode.SUBTRACT)
        with BuildLine():
            Line((-1.8145, -2.875341675), (-3.004391671, -4.066450004))
            Line((-3.004391671, -4.066450004), (-4.065608329, -3.005233346))
            Line((-4.065608329, -3.005233346), (-2.8745, -1.815341675))
            ThreePointArc((-2.8745, -1.815341675), (-3.399473913, -0.000341675), (-2.8745, 1.814658325))
            Line((-2.8745, 1.814658325), (-4.064391671, 3.005766654))
            Line((-4.064391671, 3.005766654), (-3.004391671, 4.065766654))
            Line((-3.004391671, 4.065766654), (-1.8145, 2.874658325))
            ThreePointArc((-1.8145, 2.874658325), (0, 3.399316649), (1.8145, 2.874658325))
            Line((1.8145, 2.874658325), (3.0055, 4.065658325))
            Line((3.0055, 4.065658325), (4.066608329, 3.004549996))
            Line((4.066608329, 3.004549996), (2.8755, 1.814658325))
            ThreePointArc((2.8755, 1.814658325), (3.400473913, -0.000341675), (2.8755, -1.815341675))
            Line((2.8755, -1.815341675), (4.066608329, -3.005233346))
            Line((4.066608329, -3.005233346), (3.0055, -4.066341675))
            Line((3.0055, -4.066341675), (1.8145, -2.875341675))
            ThreePointArc((1.8145, -2.875341675), (0, -3.4), (-1.8145, -2.875341675))
        make_face(mode=Mode.SUBTRACT)
        with BuildLine():
            Line((-17.9995, -15.500341675), (-17.9995, -11.800341675))
            Line((-17.9995, -11.800341675), (-11.7995, -11.800341675))
            Line((-11.7995, -11.800341675), (-11.7995, -18.000341675))
            Line((-11.7995, -18.000341675), (-15.4995, -18.000341675))
            ThreePointArc((-15.4995, -18.000341675), (-17.267266953, -17.268108628), (-17.9995, -15.500341675))
        make_face(mode=Mode.SUBTRACT)
        with BuildLine():
            Line((-11.7995, 17.999658325), (-11.7995, 11.799658325))
            Line((-11.7995, 11.799658325), (-17.9995, 11.799658325))
            Line((-17.9995, 11.799658325), (-17.9995, 15.499658325))
            ThreePointArc((-17.9995, 15.499658325), (-17.267266953, 17.267425278), (-15.4995, 17.999658325))
            Line((-15.4995, 17.999658325), (-11.7995, 17.999658325))
        make_face(mode=Mode.SUBTRACT)
    extrude(amount=-EXTRUDE_1_DEPTH)


solid = part.part
